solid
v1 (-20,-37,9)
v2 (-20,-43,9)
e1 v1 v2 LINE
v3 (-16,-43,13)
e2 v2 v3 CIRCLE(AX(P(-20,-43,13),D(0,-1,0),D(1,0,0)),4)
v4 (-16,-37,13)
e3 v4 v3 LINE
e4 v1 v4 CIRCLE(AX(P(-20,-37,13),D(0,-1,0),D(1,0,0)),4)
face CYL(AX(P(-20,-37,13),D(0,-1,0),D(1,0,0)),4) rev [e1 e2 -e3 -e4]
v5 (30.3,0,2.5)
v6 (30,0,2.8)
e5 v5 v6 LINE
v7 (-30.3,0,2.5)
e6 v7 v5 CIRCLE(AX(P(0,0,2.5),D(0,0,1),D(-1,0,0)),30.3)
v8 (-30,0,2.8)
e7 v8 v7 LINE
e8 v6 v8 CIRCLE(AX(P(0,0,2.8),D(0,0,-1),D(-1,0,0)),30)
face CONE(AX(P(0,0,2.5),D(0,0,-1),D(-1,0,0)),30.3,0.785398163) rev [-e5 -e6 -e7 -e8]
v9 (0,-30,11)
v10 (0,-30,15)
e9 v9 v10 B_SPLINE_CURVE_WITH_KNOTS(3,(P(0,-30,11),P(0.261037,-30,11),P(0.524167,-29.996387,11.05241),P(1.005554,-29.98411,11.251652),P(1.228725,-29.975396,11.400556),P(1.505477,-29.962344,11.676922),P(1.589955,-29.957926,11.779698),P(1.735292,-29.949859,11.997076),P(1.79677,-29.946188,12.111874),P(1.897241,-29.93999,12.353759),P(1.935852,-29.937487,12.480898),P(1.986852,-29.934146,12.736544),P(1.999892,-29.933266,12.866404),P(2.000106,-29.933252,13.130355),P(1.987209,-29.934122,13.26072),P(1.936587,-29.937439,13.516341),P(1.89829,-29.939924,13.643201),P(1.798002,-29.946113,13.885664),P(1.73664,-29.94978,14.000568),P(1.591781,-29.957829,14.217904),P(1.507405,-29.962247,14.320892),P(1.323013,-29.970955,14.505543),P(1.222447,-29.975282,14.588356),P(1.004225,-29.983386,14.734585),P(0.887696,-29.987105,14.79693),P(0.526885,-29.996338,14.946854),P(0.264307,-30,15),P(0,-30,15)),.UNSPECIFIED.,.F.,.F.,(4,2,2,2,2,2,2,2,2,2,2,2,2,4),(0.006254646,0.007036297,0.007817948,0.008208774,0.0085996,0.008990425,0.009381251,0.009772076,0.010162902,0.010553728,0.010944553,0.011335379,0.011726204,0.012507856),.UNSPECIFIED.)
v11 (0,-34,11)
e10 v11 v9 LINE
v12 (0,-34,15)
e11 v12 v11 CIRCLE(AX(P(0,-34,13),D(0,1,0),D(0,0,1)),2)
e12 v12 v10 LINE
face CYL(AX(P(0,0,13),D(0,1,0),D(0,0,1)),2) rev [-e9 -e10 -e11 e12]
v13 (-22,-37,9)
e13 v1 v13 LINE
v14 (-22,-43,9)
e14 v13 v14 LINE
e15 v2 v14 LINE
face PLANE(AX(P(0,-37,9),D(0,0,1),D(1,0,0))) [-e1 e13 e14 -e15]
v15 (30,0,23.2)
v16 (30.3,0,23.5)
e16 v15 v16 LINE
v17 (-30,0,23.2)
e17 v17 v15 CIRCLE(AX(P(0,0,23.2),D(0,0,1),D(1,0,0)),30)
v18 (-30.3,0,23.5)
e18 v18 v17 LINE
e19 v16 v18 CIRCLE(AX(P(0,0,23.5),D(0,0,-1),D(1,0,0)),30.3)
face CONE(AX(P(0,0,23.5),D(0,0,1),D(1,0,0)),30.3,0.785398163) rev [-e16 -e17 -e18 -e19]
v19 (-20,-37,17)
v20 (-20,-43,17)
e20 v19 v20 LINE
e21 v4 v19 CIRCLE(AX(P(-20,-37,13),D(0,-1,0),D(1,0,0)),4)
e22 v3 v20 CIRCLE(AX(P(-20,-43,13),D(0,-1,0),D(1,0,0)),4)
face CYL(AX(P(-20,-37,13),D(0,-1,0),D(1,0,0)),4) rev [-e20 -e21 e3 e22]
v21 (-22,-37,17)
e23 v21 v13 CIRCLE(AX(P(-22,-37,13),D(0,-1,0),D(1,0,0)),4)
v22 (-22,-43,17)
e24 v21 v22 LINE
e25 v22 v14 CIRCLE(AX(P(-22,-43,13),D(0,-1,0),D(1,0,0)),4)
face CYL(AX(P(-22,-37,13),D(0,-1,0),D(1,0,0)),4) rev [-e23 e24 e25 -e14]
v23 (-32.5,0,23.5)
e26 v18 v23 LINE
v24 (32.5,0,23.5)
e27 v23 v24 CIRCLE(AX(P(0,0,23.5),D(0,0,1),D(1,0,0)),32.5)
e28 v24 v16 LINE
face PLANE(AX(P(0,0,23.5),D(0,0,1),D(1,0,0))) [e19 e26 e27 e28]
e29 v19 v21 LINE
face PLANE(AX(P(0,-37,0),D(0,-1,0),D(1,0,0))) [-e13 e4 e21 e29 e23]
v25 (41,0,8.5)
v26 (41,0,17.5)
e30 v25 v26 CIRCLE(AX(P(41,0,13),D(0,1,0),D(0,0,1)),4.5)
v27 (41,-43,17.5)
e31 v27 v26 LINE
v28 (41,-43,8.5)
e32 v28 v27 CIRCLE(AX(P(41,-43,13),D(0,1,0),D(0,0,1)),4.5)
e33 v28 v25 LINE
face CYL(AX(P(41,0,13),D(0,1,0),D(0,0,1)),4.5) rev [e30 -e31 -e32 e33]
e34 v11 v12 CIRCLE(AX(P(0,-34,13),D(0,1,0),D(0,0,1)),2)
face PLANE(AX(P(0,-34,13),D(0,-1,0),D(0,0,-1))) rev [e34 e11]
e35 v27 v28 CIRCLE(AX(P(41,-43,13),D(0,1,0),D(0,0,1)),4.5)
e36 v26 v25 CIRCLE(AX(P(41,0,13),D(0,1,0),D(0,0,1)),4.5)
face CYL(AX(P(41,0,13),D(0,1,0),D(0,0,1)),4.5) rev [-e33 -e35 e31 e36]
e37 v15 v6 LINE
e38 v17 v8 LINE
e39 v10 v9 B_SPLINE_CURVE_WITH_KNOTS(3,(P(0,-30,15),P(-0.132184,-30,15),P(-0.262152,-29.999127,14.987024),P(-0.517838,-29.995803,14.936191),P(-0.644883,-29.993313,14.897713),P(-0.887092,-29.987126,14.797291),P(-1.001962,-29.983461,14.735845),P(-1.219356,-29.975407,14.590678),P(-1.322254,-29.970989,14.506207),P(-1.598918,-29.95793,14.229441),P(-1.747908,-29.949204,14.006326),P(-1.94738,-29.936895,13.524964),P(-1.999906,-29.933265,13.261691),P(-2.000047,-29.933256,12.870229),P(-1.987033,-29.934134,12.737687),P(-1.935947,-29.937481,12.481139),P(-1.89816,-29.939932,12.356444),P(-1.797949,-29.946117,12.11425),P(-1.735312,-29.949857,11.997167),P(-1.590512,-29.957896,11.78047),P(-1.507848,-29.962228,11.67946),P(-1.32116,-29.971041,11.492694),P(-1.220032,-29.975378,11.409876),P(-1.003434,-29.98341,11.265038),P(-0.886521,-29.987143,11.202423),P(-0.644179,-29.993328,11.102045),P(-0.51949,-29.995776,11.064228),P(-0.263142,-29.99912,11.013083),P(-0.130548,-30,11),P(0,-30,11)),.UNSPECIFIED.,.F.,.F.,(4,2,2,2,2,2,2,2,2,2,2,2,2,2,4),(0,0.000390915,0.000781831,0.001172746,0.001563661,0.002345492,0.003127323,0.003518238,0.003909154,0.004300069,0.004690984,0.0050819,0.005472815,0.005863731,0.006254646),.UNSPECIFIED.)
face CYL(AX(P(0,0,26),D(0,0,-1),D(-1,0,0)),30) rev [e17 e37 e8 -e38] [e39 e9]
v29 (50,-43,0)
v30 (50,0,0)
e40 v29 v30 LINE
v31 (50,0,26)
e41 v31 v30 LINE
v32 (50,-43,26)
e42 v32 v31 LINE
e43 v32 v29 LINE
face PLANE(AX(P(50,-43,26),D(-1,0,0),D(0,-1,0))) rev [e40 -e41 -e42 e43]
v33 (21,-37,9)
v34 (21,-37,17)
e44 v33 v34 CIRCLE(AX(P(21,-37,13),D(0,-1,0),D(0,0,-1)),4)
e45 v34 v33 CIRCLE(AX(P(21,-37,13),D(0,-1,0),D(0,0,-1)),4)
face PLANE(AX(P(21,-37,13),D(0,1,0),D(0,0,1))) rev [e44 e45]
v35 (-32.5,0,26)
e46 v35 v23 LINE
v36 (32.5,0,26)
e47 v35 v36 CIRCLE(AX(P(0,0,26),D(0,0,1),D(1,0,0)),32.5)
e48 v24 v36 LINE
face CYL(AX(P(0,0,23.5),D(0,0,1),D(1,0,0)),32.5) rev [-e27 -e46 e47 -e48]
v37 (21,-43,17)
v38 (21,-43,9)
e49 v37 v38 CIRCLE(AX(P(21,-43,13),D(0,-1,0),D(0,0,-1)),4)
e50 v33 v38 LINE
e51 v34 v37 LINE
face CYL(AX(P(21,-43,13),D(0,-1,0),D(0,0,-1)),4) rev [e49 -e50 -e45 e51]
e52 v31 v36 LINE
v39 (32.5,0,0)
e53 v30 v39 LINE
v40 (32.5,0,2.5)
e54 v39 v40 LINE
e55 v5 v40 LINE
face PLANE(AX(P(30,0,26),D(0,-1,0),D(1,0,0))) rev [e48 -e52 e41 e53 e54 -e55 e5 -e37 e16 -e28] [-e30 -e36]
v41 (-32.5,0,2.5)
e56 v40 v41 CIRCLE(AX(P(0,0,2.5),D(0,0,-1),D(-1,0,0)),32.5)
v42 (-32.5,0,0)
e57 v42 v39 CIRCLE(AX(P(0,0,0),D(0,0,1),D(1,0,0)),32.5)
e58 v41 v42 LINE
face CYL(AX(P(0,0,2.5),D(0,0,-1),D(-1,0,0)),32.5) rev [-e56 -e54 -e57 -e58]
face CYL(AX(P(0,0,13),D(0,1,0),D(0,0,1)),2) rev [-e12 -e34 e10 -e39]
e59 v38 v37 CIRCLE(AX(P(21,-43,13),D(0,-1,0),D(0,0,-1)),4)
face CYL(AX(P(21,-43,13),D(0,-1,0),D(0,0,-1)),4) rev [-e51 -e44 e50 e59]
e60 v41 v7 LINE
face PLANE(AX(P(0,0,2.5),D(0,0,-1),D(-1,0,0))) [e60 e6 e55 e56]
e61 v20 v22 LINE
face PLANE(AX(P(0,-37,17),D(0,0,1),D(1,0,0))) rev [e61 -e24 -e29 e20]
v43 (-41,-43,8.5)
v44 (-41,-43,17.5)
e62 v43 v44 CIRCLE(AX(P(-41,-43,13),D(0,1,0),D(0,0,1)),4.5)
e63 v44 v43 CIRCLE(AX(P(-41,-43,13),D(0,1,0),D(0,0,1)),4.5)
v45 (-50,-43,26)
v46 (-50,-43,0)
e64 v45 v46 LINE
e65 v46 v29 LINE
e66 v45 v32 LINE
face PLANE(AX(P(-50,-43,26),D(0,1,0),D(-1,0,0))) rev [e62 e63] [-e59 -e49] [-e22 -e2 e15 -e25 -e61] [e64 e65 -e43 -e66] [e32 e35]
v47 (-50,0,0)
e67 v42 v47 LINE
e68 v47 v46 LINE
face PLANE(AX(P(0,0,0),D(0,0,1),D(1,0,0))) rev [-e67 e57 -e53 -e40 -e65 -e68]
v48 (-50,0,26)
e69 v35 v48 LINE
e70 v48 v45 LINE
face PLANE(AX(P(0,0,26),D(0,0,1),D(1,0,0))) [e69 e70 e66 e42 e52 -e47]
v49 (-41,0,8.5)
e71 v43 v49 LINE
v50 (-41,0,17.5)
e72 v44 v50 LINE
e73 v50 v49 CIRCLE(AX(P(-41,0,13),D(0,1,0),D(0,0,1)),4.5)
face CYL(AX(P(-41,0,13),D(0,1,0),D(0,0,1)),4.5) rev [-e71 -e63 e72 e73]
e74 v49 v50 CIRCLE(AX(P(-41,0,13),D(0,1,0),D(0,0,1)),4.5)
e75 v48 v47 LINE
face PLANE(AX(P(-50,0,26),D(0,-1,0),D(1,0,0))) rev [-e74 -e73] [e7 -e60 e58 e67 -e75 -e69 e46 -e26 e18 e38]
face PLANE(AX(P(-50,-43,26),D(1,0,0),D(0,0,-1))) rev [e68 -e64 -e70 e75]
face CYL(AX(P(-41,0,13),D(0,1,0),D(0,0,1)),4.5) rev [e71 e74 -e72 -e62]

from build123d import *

# Parameters (mm, degrees)
BOSS_EXTRUDE1_DEPTH = 26
SKETCH2_R           = 32.5
CUT_EXTRUDE1_DEPTH  = 2.5
CUT_EXTRUDE2_START  = -2.5
SKETCH3_R           = 32.5
CUT_EXTRUDE2_DEPTH  = 2.5
CHAMFER1_SIZE       = 0.3
HOLE1_D             = 9
HOLE2_D             = 4
HOLE2_DEPTH         = 34
HOLE4_D             = 8
HOLE4_DEPTH         = 6
CUT_EXTRUDE4_DEPTH  = 6


with BuildPart() as part:
    # Sketch1 → Boss-Extrude1 (new body)
    with BuildSketch(Plane.XY):
        with BuildLine():
            Line((-50, 0), (-30, 0))
            ThreePointArc((-30, 0), (0, -30), (30, 0))
            Line((30, 0), (50, 0))
            Line((50, 0), (50, -43))
            Line((50, -43), (-50, -43))
            Line((-50, -43), (-50, 0))
        make_face()
    extrude(amount=BOSS_EXTRUDE1_DEPTH)

    # Sketch2 → Cut-Extrude1 (cut)
    with BuildSketch(Plane.XY.offset(26)):
        Circle(SKETCH2_R)
    extrude(amount=-CUT_EXTRUDE1_DEPTH, mode=Mode.SUBTRACT)

    # Sketch3 → Cut-Extrude2 (cut)
    with BuildSketch(Plane(origin=(0, 0, 0), x_dir=(-1, 0, 0), z_dir=(0, 0, -1)).offset(CUT_EXTRUDE2_START)):
        Circle(SKETCH3_R)
    extrude(amount=CUT_EXTRUDE2_DEPTH, mode=Mode.SUBTRACT)

    # Chamfer1
    chamfer1_edges = [part.edges().sort_by_distance(p)[0] for p in [
        (0, -30, 23.5),
        (0, -30, 2.5),
    ]]
    chamfer(chamfer1_edges, length=CHAMFER1_SIZE)

    # Hole1 (through all)
    with Locations(Plane(origin=(0, 0, 0), x_dir=(1, 0, 0), z_dir=(0, 1, 0))):
        with Locations((-41, -13), (41, -13)):
            Hole(HOLE1_D / 2)

    # Hole2
    with Locations(Plane(origin=(0, 0, 0), x_dir=(1, 0, 0), z_dir=(0, 1, 0))):
        with Locations((0, -13)):
            Hole(HOLE2_D / 2, depth=HOLE2_DEPTH)

    # Hole4
    with Locations(Plane(origin=(0, -43, 0), x_dir=(-1, 0, 0), z_dir=(0, -1, 0))):
        with Locations((-21, -13)):
            Hole(HOLE4_D / 2, depth=HOLE4_DEPTH)

    # Sketch11 → Cut-Extrude4 (cut)
    with BuildSketch(Plane.XZ.offset(43)):
        with BuildLine():
            Line((-20, 17), (-22, 17))
            ThreePointArc((-22, 17), (-26, 13), (-22, 9))
            Line((-22, 9), (-20, 9))
            ThreePointArc((-20, 9), (-16, 13), (-20, 17))
        make_face()
    extrude(amount=-CUT_EXTRUDE4_DEPTH, mode=Mode.SUBTRACT)


solid = part.part
